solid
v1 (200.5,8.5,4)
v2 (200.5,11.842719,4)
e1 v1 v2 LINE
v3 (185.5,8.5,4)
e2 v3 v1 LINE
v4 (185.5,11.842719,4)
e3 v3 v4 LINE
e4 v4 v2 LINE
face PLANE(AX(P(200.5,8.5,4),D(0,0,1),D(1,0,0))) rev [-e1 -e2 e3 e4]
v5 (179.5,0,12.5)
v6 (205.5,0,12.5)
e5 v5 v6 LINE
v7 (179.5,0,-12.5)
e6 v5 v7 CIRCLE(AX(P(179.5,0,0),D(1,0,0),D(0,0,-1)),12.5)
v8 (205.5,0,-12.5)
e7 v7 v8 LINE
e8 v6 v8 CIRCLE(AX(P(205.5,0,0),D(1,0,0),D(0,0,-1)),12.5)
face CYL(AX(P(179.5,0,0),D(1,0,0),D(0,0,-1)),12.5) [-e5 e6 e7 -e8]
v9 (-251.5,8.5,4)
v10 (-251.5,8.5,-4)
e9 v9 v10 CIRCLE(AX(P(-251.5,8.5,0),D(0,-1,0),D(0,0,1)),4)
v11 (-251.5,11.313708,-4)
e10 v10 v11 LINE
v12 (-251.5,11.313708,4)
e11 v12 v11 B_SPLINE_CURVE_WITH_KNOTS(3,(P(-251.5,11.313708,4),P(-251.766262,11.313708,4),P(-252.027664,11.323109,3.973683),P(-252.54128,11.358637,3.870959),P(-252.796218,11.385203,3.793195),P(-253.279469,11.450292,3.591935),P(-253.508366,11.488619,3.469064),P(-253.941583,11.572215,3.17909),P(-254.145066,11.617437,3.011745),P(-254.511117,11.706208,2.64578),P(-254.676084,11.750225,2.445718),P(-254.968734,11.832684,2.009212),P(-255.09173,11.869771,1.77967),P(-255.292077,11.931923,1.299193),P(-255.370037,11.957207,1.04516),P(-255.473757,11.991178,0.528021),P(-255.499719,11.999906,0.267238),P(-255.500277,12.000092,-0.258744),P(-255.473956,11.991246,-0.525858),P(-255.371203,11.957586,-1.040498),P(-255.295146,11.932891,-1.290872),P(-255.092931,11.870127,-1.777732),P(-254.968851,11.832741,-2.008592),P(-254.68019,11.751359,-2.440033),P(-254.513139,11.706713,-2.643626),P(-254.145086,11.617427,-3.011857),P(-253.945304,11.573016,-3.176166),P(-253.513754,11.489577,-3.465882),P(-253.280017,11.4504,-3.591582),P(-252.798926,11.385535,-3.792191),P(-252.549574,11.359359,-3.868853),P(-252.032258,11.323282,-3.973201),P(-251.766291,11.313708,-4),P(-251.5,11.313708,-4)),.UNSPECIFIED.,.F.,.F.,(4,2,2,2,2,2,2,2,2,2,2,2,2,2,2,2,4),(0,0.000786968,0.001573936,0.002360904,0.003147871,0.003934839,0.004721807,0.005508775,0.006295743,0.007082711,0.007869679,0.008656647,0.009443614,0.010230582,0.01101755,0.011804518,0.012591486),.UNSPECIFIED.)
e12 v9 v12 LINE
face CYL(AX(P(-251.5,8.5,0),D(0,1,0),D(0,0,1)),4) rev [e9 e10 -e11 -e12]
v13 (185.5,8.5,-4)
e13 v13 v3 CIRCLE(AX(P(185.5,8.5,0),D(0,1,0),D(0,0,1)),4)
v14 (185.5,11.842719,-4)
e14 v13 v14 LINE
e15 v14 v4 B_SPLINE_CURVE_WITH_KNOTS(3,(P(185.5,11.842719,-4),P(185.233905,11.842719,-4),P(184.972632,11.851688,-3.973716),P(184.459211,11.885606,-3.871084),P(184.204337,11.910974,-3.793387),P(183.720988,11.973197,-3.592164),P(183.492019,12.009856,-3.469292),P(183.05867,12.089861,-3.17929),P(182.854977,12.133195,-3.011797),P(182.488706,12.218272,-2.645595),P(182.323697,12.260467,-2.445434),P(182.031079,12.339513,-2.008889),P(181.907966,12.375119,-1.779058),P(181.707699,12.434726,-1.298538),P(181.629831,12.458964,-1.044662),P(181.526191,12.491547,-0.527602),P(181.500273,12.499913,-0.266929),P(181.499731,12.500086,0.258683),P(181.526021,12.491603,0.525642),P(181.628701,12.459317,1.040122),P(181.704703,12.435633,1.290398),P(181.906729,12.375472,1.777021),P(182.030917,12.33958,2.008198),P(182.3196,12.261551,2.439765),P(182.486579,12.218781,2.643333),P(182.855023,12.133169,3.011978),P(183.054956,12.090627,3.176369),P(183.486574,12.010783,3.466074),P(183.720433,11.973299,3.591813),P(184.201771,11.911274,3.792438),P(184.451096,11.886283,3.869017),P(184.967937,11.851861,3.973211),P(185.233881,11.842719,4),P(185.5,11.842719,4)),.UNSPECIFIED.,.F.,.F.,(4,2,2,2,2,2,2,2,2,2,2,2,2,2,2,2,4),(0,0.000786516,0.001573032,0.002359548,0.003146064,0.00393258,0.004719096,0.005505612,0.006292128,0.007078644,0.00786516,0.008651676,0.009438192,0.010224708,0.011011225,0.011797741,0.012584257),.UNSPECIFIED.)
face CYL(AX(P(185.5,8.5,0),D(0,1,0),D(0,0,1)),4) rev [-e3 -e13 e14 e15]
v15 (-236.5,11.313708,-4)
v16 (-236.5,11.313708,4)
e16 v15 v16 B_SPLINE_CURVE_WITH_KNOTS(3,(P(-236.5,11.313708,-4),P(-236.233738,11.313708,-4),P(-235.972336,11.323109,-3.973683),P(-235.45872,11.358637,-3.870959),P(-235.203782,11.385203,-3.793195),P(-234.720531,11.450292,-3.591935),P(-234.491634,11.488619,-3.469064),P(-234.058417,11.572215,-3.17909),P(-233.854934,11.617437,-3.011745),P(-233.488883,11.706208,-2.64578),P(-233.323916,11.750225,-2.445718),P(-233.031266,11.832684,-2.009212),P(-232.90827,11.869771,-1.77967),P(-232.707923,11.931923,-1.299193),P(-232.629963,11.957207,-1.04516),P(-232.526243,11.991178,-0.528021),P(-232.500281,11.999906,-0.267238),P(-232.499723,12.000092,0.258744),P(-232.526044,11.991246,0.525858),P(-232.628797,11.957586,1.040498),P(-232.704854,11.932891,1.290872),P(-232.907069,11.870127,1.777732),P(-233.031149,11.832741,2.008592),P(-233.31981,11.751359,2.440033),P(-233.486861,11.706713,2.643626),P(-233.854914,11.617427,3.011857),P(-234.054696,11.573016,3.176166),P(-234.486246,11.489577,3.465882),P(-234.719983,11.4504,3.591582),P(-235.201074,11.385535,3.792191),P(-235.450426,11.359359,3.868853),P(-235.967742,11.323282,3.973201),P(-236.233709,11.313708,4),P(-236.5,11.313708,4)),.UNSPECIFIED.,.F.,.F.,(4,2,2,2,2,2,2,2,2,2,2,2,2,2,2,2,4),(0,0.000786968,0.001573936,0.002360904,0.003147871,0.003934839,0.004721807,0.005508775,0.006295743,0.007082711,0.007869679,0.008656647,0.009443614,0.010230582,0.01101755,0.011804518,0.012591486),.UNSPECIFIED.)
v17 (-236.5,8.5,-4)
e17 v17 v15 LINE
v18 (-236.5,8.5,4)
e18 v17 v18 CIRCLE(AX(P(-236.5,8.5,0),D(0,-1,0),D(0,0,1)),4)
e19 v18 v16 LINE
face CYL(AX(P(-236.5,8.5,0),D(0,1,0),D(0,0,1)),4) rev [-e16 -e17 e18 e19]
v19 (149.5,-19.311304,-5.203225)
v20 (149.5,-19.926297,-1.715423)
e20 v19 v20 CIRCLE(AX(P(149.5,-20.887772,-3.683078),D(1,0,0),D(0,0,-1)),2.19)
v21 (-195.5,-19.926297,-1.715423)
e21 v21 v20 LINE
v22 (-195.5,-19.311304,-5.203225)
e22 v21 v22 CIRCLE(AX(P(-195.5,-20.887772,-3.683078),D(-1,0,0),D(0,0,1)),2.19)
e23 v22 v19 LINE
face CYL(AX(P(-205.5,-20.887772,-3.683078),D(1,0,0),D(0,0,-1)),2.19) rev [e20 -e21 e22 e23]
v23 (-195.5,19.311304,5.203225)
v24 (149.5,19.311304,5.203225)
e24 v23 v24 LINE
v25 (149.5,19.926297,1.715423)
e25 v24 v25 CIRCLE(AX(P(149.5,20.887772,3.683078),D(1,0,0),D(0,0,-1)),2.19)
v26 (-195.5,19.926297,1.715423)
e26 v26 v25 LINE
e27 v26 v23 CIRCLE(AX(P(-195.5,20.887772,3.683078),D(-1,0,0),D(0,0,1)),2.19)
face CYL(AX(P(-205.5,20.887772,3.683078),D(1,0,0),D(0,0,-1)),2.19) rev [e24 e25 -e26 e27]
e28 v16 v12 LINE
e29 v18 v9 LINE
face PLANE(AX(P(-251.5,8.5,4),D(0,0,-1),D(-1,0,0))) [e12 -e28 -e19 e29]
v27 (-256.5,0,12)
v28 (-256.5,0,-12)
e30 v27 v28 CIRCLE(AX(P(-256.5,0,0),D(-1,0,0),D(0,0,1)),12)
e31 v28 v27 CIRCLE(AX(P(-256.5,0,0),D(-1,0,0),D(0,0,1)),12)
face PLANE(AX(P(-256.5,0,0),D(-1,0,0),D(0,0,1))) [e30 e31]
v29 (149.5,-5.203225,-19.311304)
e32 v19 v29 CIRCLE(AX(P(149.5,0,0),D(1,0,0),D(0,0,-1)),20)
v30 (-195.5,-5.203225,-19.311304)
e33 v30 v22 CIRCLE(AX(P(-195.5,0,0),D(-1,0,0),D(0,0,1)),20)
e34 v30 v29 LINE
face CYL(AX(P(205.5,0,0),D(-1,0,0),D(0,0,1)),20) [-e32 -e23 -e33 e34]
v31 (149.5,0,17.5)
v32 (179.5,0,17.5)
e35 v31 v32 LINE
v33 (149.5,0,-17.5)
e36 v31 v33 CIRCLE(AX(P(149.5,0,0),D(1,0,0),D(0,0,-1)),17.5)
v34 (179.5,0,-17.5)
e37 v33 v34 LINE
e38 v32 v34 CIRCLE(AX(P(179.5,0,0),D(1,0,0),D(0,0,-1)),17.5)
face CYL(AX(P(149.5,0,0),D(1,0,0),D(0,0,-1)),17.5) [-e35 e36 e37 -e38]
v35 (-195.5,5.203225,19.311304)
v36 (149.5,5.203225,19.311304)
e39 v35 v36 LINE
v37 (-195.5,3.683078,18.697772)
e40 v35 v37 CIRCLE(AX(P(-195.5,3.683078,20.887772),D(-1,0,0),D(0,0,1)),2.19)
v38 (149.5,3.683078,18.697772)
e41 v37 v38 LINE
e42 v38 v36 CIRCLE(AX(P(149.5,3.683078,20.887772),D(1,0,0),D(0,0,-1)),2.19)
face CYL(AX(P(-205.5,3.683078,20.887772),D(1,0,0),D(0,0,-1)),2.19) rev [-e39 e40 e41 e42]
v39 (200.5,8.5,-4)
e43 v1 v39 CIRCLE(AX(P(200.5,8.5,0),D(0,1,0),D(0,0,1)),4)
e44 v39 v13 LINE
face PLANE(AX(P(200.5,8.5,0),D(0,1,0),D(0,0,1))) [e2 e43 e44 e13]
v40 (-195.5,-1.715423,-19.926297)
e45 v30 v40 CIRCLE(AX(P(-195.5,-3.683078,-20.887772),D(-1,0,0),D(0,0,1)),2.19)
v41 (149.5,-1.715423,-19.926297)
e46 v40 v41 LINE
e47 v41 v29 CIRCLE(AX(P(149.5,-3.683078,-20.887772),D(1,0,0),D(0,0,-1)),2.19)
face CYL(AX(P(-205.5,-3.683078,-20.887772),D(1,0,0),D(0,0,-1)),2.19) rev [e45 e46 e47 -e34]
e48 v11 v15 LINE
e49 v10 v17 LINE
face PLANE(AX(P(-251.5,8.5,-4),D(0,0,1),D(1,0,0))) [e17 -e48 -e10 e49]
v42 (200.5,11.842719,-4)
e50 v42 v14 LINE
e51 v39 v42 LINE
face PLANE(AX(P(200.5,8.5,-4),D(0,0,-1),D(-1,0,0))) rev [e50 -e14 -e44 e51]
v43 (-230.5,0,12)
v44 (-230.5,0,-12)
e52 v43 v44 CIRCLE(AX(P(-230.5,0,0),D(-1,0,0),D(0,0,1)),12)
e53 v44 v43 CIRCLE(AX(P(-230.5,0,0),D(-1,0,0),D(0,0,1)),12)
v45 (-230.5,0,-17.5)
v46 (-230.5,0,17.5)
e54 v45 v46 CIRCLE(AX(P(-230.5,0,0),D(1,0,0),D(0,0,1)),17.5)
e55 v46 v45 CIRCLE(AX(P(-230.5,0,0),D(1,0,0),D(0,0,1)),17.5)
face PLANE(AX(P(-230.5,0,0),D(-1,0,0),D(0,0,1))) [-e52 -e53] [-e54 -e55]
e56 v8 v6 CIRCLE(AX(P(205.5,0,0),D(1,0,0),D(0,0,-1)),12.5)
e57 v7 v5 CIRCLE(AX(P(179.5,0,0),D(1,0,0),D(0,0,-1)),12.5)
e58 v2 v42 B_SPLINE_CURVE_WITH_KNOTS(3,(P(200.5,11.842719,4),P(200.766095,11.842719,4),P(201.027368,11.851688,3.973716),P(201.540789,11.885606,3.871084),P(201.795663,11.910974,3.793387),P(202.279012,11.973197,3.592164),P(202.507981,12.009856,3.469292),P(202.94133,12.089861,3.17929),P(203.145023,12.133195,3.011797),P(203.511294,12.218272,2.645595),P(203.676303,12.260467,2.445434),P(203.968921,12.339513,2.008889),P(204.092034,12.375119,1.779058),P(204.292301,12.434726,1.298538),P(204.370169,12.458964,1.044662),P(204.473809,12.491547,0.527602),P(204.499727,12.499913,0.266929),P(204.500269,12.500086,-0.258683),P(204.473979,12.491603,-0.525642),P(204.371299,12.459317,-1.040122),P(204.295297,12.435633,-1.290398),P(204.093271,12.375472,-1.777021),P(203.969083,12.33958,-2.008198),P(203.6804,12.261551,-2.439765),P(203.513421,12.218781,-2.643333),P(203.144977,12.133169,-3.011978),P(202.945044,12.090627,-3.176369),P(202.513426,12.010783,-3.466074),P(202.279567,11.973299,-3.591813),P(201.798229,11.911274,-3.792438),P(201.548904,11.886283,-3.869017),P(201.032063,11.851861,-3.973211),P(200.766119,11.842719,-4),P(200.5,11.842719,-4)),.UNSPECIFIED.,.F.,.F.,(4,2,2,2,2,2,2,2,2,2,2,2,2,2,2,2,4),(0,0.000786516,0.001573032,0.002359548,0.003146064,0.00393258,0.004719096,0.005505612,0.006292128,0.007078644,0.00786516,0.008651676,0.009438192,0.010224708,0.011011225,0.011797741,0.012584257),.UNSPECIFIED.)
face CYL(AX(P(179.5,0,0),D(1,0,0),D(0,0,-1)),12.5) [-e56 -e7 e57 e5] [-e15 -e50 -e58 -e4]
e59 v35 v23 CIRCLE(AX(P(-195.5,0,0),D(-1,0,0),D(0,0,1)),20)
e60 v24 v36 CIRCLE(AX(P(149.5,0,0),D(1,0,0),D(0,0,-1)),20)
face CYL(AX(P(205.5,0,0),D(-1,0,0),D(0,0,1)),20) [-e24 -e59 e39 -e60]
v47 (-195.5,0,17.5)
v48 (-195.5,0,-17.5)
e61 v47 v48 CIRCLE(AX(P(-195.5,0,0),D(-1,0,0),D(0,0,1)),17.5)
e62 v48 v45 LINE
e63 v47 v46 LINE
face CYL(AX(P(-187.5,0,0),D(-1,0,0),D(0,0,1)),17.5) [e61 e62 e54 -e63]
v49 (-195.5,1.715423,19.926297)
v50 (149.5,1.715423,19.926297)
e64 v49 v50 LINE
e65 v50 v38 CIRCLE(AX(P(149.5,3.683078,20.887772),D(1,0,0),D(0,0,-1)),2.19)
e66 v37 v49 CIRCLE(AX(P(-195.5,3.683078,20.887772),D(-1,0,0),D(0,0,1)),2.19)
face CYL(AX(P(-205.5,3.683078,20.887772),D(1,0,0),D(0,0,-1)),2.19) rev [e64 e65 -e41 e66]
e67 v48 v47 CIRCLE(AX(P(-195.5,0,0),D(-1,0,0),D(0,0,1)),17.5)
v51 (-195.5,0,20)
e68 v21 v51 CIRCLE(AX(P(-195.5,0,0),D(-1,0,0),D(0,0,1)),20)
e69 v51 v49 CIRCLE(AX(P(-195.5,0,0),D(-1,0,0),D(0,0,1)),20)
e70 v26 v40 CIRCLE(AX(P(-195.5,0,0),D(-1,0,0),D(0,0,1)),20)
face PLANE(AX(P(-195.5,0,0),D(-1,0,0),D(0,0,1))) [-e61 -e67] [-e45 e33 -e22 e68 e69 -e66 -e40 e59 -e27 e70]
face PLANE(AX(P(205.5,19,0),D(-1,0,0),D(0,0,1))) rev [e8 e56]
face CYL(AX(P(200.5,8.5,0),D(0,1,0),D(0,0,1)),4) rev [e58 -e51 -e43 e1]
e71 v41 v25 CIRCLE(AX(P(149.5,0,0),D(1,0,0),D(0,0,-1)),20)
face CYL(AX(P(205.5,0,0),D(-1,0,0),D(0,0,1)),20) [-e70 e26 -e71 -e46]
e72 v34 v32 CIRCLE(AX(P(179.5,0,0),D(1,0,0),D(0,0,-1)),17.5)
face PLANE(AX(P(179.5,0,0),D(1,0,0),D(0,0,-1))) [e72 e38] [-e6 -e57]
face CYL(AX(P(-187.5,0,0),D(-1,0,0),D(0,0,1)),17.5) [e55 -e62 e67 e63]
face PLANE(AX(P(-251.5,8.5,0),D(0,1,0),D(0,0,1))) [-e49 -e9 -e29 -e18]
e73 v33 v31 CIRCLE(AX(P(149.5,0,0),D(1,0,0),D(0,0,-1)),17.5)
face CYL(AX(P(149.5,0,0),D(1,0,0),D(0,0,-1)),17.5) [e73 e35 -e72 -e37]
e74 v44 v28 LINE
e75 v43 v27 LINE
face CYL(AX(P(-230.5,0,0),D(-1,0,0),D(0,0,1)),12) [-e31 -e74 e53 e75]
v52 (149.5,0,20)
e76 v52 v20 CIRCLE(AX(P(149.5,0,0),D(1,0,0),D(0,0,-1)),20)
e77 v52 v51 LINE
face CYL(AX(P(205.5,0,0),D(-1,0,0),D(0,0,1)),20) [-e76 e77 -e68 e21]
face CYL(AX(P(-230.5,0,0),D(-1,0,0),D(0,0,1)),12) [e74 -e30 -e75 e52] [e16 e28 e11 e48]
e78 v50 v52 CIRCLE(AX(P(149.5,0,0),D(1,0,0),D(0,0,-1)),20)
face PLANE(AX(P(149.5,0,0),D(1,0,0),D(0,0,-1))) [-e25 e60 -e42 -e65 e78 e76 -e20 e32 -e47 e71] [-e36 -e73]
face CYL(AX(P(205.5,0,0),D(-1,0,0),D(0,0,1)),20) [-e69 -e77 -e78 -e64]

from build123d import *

# Parameters (mm, degrees)
CUT_EXTRUDE_1_DEPTH      = 205.5
CUT_EXTRUDE_1_DEPTH_BACK = 205.5
SKETCH_2_R               = 40
SKETCH_3_OUTSIDE_W       = 124.974
SKETCH_3_OUTSIDE_H       = 124.974
SKETCH_3_OUTSIDE_R       = 17.5
CUT_EXTRUDE_2_DEPTH      = 18
SKETCH_4_OUTSIDE_W       = 124.974
SKETCH_4_OUTSIDE_H       = 124.974
SKETCH_4_OUTSIDE_R       = 12.5
CUT_EXTRUDE_3_DEPTH      = 26
SKETCH_5_OUTSIDE_W       = 124.974
SKETCH_5_OUTSIDE_H       = 124.974
SKETCH_5_OUTSIDE_R       = 17.5
CUT_EXTRUDE_4_DEPTH      = 30
CUT_EXTRUDE_5_DEPTH      = 4
SKETCH_7_R               = 17.5
EXTRUDE_1_DEPTH          = 51
SKETCH_9_OUTSIDE_W       = 135.09
SKETCH_9_OUTSIDE_H       = 135.09
SKETCH_9_OUTSIDE_R       = 12
CUT_EXTRUDE_7_DEPTH      = 26
MOVE_FACE_1_BY           = 8


with BuildPart() as part:
    # 草图1 → 旋转1 (revolve)
    with BuildSketch(Plane.XY, mode=Mode.PRIVATE) as revolve_1_sk:
        Polygon((-205.5, 0), (-205.5, 19), (-204.5, 20), (204.5, 20), (205.5, 19), (205.5, 0), align=None)
    revolve(revolve_1_sk.sketch.rotate(Axis((205.5, 0, 0), (-1, 0, 0)), 270), axis=Axis((205.5, 0, 0), (-1, 0, 0)))

    # 草图2 → 切除-拉伸1 (cut, two sides: drawn at the far end of the back side and taken through both)
    with BuildSketch(Plane(origin=(0, 0, 0), x_dir=(0, 0, -1), z_dir=(1, 0, 0)).offset(-CUT_EXTRUDE_1_DEPTH_BACK)):
        Circle(SKETCH_2_R)
        with BuildLine():
            ThreePointArc((-19.926297295, 1.715423015), (-14.142135624, -14.142135624), (1.715423015, -19.926297295))
            ThreePointArc((1.715423015, -19.926297295), (3.302788339, -18.731043462), (5.203224708, -19.311303753))
            ThreePointArc((5.203224708, -19.311303753), (14.142135624, -14.142135624), (19.311303753, -5.203224708))
            ThreePointArc((19.311303753, -5.203224708), (18.731043462, -3.302788339), (19.926297295, -1.715423015))
            ThreePointArc((19.926297295, -1.715423015), (14.142135624, 14.142135624), (-1.715423015, 19.926297295))
            ThreePointArc((-1.715423015, 19.926297295), (-3.302788339, 18.731043462), (-5.203224708, 19.311303753))
            ThreePointArc((-5.203224708, 19.311303753), (-14.142135624, 14.142135624), (-19.311303753, 5.203224708))
            ThreePointArc((-19.311303753, 5.203224708), (-18.731043462, 3.302788339), (-19.926297295, 1.715423015))
        make_face(mode=Mode.SUBTRACT)
    extrude(amount=CUT_EXTRUDE_1_DEPTH + CUT_EXTRUDE_1_DEPTH_BACK, mode=Mode.SUBTRACT)

    # 草图3 outside → 切除-拉伸2 (cut)
    with BuildSketch(Plane.ZY.offset(205.5)):
        Rectangle(SKETCH_3_OUTSIDE_W, SKETCH_3_OUTSIDE_H)
        Circle(SKETCH_3_OUTSIDE_R, mode=Mode.SUBTRACT)
    extrude(amount=-CUT_EXTRUDE_2_DEPTH, mode=Mode.SUBTRACT)

    # 草图4 outside → 切除-拉伸3 (cut)
    with BuildSketch(Plane(origin=(205.5, 0, 0), x_dir=(0, 0, -1), z_dir=(1, 0, 0))):
        Rectangle(SKETCH_4_OUTSIDE_W, SKETCH_4_OUTSIDE_H)
        Circle(SKETCH_4_OUTSIDE_R, mode=Mode.SUBTRACT)
    extrude(amount=-CUT_EXTRUDE_3_DEPTH, mode=Mode.SUBTRACT)

    # 草图5 outside → 切除-拉伸4 (cut)
    with BuildSketch(Plane(origin=(179.5, 0, 0), x_dir=(0, 0, -1), z_dir=(1, 0, 0))):
        Rectangle(SKETCH_5_OUTSIDE_W, SKETCH_5_OUTSIDE_H)
        with Locations(Location((0, 0, 0), (0, 0, 180))):
            Circle(SKETCH_5_OUTSIDE_R, mode=Mode.SUBTRACT)
    extrude(amount=-CUT_EXTRUDE_4_DEPTH, mode=Mode.SUBTRACT)

    # 草图6 → 切除-拉伸5 (cut)
    with BuildSketch(Plane(origin=(0, 12.5, 0), x_dir=(1, 0, 0), z_dir=(0, 1, 0))):
        with BuildLine():
            Line((200.5, -4), (185.5, -4))
            ThreePointArc((185.5, -4), (181.5, 0), (185.5, 4))
            Line((185.5, 4), (200.5, 4))
            ThreePointArc((200.5, 4), (204.5, 0), (200.5, -4))
        make_face()
    cut_extrude_5 = extrude(amount=-CUT_EXTRUDE_5_DEPTH, mode=Mode.SUBTRACT)

    # 草图7 → 凸台-拉伸1 (add)
    with BuildSketch(Plane.ZY.offset(205.5)):
        Circle(SKETCH_7_R)
    extrude(amount=EXTRUDE_1_DEPTH)

    # 草图9 outside → 切除-拉伸7 (cut)
    with BuildSketch(Plane.ZY.offset(256.5)):
        Rectangle(SKETCH_9_OUTSIDE_W, SKETCH_9_OUTSIDE_H)
        Circle(SKETCH_9_OUTSIDE_R, mode=Mode.SUBTRACT)
    extrude(amount=-CUT_EXTRUDE_7_DEPTH, mode=Mode.SUBTRACT)

    # 镜向1: 切除-拉伸5 across plane
    add(cut_extrude_5.mirror(Plane.ZY.offset(25.5)), mode=Mode.SUBTRACT)

    # Move Face 1: a face moved outward by 8.0
    extrude(part.faces().sort_by_distance((-187.5, -16, -10))[0], amount=MOVE_FACE_1_BY, dir=(-1, 0, 0))


solid = part.part
